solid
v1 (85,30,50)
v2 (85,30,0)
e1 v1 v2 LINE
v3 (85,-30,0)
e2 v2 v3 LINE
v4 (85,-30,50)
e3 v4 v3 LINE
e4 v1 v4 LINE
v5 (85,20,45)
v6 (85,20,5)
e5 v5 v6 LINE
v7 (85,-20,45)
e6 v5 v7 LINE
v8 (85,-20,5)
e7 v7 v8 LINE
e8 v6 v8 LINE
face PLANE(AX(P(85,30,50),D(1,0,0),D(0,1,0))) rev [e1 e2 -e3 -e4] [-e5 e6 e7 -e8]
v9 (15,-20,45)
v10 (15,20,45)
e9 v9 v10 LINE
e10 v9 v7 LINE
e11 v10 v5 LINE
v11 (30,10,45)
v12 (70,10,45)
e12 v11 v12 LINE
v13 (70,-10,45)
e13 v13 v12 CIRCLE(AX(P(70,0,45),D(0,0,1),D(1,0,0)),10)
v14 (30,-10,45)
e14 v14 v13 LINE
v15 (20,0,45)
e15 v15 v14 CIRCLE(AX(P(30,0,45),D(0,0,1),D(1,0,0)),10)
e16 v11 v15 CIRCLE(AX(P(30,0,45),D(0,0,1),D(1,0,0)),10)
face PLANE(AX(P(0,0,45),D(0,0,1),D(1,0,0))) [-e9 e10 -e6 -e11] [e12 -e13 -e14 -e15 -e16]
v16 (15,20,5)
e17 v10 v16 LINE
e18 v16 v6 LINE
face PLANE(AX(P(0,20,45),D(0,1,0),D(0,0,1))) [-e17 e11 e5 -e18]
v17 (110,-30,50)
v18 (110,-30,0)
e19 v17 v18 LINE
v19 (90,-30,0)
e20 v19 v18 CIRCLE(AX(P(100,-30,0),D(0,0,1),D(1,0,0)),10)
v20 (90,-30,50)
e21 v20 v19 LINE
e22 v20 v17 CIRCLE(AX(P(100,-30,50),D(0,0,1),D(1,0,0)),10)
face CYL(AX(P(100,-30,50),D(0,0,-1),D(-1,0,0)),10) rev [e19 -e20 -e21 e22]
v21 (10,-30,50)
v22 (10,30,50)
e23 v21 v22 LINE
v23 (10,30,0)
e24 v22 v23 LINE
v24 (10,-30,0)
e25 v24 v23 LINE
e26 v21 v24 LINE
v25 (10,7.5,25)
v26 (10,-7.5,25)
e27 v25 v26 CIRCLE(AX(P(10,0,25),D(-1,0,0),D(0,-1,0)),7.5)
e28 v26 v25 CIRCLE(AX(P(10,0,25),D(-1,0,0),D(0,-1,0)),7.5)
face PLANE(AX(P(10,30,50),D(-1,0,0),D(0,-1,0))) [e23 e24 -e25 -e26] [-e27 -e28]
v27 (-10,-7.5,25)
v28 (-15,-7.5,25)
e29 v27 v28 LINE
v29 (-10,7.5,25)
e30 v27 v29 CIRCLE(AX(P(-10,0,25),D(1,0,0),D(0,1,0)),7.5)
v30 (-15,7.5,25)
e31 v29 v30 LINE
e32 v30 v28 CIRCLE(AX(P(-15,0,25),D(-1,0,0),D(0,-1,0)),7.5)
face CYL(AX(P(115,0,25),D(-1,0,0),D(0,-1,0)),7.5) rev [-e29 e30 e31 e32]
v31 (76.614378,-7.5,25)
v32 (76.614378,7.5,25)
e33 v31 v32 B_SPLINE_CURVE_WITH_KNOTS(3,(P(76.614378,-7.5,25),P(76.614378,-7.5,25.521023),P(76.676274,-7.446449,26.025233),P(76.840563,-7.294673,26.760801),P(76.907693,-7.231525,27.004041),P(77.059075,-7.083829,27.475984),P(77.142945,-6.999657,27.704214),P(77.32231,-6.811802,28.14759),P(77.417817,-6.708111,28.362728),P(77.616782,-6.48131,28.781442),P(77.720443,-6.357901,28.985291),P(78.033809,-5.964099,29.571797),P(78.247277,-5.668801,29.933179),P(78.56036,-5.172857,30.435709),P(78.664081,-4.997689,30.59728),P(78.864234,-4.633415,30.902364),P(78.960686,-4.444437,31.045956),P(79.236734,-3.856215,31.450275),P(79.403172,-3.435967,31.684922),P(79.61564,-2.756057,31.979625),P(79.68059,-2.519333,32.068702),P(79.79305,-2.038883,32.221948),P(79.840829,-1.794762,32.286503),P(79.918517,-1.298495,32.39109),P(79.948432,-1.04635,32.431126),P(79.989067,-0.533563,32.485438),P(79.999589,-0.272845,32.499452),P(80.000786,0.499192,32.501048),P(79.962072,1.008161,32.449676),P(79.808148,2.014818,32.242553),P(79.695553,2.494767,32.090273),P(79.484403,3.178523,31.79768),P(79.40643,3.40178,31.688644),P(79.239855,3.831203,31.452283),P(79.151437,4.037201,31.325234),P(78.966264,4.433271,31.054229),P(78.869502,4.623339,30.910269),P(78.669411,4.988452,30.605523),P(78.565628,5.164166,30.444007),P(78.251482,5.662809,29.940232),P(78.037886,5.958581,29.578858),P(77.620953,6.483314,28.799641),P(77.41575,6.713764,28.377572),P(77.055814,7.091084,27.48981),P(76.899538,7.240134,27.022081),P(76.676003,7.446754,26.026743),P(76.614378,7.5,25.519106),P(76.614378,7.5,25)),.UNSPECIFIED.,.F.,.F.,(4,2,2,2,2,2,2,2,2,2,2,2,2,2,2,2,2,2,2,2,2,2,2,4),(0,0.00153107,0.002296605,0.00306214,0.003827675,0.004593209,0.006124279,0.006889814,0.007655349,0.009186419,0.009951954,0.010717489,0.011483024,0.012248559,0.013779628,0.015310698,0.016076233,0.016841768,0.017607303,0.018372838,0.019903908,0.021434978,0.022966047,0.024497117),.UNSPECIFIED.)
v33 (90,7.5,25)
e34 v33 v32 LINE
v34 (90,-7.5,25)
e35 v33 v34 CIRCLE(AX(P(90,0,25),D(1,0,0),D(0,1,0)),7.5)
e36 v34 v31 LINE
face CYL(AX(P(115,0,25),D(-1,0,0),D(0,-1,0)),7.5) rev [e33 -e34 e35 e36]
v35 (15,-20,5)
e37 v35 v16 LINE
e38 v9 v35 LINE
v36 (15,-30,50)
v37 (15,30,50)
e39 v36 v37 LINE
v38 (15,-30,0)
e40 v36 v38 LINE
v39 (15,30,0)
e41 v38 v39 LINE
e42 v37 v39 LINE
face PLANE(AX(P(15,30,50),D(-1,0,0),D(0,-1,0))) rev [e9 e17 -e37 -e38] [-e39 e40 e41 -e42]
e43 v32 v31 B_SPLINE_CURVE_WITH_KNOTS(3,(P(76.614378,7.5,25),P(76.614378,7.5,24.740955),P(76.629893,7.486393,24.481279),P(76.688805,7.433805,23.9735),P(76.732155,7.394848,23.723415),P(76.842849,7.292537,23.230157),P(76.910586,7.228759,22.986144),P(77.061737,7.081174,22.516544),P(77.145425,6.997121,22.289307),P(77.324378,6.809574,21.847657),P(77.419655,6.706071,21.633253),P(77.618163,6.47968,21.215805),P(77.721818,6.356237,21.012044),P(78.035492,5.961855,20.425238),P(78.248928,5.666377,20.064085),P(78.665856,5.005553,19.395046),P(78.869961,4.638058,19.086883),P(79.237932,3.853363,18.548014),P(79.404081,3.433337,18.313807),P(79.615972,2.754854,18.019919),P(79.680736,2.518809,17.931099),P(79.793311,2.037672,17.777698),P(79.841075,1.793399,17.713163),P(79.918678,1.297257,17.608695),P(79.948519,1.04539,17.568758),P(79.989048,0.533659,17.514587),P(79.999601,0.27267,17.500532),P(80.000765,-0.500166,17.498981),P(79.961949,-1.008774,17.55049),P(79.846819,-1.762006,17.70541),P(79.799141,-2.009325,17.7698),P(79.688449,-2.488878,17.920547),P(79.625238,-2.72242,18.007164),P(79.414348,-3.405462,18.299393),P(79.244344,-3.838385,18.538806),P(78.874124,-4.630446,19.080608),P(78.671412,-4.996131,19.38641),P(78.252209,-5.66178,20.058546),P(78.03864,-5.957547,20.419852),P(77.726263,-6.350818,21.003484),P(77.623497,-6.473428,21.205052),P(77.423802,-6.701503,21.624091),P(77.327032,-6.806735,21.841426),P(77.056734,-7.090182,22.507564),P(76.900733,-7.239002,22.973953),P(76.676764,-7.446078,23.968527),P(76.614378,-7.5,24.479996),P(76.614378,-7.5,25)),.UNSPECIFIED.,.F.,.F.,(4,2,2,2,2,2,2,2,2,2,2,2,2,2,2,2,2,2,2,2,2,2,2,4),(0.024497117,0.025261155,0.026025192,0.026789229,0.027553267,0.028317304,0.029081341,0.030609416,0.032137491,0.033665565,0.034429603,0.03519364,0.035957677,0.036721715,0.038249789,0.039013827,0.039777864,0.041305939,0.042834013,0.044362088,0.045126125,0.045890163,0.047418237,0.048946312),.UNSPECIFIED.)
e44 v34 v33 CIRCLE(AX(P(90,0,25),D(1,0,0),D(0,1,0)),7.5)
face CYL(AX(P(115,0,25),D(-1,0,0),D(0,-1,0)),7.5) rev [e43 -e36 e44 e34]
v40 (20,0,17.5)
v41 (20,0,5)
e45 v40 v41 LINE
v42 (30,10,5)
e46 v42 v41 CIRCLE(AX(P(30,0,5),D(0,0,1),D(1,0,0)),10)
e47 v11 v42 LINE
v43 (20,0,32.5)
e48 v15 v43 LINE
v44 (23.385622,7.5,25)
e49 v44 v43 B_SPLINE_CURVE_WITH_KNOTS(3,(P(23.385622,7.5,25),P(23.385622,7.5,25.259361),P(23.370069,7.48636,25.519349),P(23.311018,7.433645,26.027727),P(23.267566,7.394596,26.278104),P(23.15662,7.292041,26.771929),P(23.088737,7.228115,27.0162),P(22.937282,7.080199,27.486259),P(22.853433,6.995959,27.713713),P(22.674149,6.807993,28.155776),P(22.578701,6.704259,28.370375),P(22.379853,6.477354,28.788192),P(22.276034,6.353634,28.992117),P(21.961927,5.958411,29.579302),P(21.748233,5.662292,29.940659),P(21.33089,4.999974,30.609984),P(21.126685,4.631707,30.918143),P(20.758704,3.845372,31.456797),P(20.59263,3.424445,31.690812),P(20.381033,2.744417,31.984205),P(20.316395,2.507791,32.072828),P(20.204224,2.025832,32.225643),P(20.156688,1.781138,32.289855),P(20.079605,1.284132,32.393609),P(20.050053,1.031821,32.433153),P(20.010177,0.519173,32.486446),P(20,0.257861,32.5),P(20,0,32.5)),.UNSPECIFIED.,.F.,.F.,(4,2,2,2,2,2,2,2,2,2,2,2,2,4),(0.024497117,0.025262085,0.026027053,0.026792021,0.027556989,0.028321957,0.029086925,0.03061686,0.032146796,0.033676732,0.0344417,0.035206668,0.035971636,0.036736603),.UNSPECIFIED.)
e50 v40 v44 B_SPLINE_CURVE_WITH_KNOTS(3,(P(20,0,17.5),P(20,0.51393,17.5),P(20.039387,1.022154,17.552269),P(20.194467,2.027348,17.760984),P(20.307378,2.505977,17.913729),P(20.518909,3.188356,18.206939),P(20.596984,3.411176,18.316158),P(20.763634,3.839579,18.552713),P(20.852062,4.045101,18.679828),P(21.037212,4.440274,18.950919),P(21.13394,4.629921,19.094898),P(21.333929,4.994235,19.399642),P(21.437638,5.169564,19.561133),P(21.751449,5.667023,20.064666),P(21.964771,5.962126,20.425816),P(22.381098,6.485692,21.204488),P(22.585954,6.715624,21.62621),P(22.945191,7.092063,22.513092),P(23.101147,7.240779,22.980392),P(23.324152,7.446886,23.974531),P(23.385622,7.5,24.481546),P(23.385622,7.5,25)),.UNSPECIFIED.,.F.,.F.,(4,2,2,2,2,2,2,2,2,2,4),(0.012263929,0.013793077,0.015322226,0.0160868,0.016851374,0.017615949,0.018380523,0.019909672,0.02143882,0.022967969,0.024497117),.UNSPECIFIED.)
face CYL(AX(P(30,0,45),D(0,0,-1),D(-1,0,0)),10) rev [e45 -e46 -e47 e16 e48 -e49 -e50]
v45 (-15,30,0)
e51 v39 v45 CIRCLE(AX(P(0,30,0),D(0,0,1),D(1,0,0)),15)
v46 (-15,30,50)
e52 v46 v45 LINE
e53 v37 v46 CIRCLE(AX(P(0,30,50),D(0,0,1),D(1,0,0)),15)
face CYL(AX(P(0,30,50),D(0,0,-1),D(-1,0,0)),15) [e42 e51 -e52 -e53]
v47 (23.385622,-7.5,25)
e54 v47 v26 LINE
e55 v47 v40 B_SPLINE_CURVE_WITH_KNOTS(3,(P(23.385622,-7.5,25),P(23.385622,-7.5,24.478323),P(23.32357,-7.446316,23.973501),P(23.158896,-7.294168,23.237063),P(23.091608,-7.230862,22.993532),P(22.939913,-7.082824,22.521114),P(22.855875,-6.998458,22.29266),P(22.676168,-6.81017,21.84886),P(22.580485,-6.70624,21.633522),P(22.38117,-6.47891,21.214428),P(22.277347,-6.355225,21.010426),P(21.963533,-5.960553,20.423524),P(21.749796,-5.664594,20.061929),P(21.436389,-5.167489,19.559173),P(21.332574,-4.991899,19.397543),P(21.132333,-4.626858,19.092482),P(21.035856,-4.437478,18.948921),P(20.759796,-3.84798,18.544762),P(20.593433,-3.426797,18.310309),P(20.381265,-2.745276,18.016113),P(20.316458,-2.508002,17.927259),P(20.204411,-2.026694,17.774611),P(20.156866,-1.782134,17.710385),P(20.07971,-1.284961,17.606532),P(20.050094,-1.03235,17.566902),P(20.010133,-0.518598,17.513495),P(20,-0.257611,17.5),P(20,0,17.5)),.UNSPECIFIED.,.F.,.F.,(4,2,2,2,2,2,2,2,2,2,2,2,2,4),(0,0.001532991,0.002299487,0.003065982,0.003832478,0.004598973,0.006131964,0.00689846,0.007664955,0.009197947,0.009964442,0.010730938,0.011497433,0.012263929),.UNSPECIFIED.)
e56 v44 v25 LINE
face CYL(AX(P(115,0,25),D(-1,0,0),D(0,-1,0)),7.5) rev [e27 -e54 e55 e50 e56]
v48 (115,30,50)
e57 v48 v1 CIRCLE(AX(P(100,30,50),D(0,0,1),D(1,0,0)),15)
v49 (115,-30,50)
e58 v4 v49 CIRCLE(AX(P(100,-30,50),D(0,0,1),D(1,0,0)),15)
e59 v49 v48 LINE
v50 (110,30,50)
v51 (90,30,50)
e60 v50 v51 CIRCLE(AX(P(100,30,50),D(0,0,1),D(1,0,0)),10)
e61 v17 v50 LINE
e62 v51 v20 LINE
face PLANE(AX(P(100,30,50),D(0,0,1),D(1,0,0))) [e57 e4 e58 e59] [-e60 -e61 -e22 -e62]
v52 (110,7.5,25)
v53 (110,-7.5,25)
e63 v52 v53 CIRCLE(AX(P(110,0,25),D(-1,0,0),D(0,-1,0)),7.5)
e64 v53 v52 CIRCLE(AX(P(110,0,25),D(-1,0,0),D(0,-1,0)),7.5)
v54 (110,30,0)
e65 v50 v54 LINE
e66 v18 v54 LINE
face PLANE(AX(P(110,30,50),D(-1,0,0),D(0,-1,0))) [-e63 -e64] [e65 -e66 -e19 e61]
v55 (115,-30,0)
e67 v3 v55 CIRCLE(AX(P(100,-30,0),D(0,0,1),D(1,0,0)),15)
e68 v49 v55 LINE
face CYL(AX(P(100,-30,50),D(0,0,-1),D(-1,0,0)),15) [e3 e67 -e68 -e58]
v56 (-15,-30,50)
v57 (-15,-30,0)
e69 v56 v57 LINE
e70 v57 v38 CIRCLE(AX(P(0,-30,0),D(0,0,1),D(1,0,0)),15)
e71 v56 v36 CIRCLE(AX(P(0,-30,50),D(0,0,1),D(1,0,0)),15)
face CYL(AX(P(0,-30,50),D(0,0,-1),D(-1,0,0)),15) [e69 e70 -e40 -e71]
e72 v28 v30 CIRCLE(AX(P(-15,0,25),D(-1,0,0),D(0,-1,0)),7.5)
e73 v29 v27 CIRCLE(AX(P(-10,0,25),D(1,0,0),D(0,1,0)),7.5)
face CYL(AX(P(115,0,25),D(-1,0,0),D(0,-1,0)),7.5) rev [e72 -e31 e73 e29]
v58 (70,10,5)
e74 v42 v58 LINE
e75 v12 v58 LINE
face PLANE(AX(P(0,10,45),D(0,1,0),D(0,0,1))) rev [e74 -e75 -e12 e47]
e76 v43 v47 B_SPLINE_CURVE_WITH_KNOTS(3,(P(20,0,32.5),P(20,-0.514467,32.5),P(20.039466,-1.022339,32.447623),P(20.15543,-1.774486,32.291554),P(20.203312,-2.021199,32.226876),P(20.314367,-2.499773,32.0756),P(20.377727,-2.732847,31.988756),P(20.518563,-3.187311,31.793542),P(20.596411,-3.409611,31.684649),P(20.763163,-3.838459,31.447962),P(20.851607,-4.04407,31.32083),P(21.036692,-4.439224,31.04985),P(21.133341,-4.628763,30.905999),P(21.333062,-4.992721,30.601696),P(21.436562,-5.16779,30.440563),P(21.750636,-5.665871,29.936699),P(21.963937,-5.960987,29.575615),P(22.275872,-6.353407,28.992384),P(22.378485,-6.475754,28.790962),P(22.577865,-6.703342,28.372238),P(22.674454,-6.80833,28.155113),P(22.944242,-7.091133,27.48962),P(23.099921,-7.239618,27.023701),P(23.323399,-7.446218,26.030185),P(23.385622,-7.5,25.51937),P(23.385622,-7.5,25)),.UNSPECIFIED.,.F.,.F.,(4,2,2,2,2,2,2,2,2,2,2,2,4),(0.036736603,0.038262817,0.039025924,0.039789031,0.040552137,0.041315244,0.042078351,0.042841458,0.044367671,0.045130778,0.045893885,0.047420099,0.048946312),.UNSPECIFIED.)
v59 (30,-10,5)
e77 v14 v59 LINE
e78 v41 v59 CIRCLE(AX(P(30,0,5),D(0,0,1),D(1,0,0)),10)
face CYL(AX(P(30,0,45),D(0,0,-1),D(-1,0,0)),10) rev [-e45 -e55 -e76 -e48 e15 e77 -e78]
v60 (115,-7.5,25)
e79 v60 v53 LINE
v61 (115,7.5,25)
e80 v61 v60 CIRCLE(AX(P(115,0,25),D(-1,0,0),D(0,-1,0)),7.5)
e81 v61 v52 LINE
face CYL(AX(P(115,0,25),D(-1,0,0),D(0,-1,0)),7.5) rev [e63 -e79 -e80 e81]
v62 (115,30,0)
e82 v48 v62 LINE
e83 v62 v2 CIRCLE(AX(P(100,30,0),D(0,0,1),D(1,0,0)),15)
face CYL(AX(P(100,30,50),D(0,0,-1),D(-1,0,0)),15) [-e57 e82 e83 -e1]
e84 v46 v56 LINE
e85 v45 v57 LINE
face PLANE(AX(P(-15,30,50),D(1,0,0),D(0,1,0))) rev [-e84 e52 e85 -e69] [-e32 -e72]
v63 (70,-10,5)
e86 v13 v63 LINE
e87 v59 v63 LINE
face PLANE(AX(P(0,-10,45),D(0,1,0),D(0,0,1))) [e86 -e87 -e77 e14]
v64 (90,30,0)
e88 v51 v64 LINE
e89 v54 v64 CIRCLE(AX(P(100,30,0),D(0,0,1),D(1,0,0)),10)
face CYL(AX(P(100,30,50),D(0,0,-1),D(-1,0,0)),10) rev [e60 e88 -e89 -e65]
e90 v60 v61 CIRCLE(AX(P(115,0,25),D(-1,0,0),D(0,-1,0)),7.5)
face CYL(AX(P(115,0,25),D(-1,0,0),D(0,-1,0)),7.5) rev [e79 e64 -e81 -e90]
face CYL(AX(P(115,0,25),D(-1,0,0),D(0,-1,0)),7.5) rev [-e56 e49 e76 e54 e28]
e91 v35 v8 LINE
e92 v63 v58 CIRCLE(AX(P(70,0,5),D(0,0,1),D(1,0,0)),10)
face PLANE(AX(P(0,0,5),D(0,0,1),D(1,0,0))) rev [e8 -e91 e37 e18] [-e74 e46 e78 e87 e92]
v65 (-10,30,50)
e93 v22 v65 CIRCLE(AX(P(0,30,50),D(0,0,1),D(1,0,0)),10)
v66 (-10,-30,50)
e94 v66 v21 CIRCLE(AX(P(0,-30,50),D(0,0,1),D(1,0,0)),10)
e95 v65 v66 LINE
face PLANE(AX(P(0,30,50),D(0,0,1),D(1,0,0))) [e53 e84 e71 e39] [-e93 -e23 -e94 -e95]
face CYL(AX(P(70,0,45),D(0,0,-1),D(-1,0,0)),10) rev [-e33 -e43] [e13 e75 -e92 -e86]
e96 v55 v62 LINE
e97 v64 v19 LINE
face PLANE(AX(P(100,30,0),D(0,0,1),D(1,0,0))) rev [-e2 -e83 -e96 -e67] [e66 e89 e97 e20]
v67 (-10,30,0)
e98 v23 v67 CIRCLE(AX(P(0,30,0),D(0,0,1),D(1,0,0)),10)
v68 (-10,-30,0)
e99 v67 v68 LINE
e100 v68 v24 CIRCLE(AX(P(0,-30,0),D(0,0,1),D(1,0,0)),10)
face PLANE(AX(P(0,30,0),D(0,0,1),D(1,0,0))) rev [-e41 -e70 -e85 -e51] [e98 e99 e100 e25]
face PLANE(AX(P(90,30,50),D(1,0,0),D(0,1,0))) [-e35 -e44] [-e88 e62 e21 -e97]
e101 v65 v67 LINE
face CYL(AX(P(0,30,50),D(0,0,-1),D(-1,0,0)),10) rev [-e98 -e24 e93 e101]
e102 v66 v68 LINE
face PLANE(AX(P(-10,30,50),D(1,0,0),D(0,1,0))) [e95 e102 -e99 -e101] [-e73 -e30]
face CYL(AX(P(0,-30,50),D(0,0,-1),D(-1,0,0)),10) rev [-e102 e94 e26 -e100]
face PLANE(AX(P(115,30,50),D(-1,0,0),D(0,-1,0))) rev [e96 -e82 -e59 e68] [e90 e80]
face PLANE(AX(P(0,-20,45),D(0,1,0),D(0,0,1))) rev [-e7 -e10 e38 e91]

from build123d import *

# Parameters (mm, degrees)
END_PLATES_DEPTH     = 50
END_PLATES_2_DEPTH   = 50
CENTRE_WEB_PROFILE_W = 70
CENTRE_WEB_PROFILE_H = 40
CENTRE_WEB_DEPTH     = 20
CROSS_HOLE_SKETCH_R  = 7.5
CROSS_HOLE_DEPTH     = 147.372811683


with BuildPart() as part:
    # End Plates Profile → End Plates (new body)
    with BuildSketch(Plane.XY):
        with BuildLine():
            Line((15, 30), (15, -30))
            ThreePointArc((15, -30), (0, -45), (-15, -30))
            Line((-15, -30), (-15, 30))
            ThreePointArc((-15, 30), (0, 45), (15, 30))
        make_face()
        with BuildLine():
            Line((10, 30), (10, -30))
            ThreePointArc((10, -30), (0, -40), (-10, -30))
            Line((-10, -30), (-10, 30))
            ThreePointArc((-10, 30), (0, 40), (10, 30))
        make_face(mode=Mode.SUBTRACT)
    extrude(amount=END_PLATES_DEPTH)



with BuildPart() as body_2:
    # End Plates Profile → End Plates 2 (new body)
    with BuildSketch(Plane.XY):
        with BuildLine():
            Line((115, 30), (115, -30))
            ThreePointArc((115, -30), (100, -45), (85, -30))
            Line((85, -30), (85, 30))
            ThreePointArc((85, 30), (100, 45), (115, 30))
        make_face()
        with BuildLine():
            Line((110, 30), (110, -30))
            ThreePointArc((110, -30), (100, -40), (90, -30))
            Line((90, -30), (90, 30))
            ThreePointArc((90, 30), (100, 40), (110, 30))
        make_face(mode=Mode.SUBTRACT)
    extrude(amount=END_PLATES_2_DEPTH)


with BuildPart() as part_1:
    add(part.part)

    add(body_2.part)  # Centre Web merges body 2
    # Centre Web Profile → Centre Web (add, symmetric)
    with BuildSketch(Plane.XY.offset(25)):
        with Locations((50, 0)):
            Rectangle(CENTRE_WEB_PROFILE_W, CENTRE_WEB_PROFILE_H)
        with BuildLine():
            ThreePointArc((70, -10), (80, 0), (70, 10))
            Line((70, 10), (30, 10))
            ThreePointArc((30, 10), (20, 0), (30, -10))
            Line((30, -10), (70, -10))
        make_face(mode=Mode.SUBTRACT)
    extrude(amount=CENTRE_WEB_DEPTH, both=True)

    # Cross Hole Sketch → Cross Hole (cut, through all)
    with BuildSketch(Plane.ZY.offset(15)):
        with Locations(Location((25, 0, 0), (0, 0, 270))):
            Circle(CROSS_HOLE_SKETCH_R)
    extrude(amount=-CROSS_HOLE_DEPTH, mode=Mode.SUBTRACT)


solid = part_1.part
